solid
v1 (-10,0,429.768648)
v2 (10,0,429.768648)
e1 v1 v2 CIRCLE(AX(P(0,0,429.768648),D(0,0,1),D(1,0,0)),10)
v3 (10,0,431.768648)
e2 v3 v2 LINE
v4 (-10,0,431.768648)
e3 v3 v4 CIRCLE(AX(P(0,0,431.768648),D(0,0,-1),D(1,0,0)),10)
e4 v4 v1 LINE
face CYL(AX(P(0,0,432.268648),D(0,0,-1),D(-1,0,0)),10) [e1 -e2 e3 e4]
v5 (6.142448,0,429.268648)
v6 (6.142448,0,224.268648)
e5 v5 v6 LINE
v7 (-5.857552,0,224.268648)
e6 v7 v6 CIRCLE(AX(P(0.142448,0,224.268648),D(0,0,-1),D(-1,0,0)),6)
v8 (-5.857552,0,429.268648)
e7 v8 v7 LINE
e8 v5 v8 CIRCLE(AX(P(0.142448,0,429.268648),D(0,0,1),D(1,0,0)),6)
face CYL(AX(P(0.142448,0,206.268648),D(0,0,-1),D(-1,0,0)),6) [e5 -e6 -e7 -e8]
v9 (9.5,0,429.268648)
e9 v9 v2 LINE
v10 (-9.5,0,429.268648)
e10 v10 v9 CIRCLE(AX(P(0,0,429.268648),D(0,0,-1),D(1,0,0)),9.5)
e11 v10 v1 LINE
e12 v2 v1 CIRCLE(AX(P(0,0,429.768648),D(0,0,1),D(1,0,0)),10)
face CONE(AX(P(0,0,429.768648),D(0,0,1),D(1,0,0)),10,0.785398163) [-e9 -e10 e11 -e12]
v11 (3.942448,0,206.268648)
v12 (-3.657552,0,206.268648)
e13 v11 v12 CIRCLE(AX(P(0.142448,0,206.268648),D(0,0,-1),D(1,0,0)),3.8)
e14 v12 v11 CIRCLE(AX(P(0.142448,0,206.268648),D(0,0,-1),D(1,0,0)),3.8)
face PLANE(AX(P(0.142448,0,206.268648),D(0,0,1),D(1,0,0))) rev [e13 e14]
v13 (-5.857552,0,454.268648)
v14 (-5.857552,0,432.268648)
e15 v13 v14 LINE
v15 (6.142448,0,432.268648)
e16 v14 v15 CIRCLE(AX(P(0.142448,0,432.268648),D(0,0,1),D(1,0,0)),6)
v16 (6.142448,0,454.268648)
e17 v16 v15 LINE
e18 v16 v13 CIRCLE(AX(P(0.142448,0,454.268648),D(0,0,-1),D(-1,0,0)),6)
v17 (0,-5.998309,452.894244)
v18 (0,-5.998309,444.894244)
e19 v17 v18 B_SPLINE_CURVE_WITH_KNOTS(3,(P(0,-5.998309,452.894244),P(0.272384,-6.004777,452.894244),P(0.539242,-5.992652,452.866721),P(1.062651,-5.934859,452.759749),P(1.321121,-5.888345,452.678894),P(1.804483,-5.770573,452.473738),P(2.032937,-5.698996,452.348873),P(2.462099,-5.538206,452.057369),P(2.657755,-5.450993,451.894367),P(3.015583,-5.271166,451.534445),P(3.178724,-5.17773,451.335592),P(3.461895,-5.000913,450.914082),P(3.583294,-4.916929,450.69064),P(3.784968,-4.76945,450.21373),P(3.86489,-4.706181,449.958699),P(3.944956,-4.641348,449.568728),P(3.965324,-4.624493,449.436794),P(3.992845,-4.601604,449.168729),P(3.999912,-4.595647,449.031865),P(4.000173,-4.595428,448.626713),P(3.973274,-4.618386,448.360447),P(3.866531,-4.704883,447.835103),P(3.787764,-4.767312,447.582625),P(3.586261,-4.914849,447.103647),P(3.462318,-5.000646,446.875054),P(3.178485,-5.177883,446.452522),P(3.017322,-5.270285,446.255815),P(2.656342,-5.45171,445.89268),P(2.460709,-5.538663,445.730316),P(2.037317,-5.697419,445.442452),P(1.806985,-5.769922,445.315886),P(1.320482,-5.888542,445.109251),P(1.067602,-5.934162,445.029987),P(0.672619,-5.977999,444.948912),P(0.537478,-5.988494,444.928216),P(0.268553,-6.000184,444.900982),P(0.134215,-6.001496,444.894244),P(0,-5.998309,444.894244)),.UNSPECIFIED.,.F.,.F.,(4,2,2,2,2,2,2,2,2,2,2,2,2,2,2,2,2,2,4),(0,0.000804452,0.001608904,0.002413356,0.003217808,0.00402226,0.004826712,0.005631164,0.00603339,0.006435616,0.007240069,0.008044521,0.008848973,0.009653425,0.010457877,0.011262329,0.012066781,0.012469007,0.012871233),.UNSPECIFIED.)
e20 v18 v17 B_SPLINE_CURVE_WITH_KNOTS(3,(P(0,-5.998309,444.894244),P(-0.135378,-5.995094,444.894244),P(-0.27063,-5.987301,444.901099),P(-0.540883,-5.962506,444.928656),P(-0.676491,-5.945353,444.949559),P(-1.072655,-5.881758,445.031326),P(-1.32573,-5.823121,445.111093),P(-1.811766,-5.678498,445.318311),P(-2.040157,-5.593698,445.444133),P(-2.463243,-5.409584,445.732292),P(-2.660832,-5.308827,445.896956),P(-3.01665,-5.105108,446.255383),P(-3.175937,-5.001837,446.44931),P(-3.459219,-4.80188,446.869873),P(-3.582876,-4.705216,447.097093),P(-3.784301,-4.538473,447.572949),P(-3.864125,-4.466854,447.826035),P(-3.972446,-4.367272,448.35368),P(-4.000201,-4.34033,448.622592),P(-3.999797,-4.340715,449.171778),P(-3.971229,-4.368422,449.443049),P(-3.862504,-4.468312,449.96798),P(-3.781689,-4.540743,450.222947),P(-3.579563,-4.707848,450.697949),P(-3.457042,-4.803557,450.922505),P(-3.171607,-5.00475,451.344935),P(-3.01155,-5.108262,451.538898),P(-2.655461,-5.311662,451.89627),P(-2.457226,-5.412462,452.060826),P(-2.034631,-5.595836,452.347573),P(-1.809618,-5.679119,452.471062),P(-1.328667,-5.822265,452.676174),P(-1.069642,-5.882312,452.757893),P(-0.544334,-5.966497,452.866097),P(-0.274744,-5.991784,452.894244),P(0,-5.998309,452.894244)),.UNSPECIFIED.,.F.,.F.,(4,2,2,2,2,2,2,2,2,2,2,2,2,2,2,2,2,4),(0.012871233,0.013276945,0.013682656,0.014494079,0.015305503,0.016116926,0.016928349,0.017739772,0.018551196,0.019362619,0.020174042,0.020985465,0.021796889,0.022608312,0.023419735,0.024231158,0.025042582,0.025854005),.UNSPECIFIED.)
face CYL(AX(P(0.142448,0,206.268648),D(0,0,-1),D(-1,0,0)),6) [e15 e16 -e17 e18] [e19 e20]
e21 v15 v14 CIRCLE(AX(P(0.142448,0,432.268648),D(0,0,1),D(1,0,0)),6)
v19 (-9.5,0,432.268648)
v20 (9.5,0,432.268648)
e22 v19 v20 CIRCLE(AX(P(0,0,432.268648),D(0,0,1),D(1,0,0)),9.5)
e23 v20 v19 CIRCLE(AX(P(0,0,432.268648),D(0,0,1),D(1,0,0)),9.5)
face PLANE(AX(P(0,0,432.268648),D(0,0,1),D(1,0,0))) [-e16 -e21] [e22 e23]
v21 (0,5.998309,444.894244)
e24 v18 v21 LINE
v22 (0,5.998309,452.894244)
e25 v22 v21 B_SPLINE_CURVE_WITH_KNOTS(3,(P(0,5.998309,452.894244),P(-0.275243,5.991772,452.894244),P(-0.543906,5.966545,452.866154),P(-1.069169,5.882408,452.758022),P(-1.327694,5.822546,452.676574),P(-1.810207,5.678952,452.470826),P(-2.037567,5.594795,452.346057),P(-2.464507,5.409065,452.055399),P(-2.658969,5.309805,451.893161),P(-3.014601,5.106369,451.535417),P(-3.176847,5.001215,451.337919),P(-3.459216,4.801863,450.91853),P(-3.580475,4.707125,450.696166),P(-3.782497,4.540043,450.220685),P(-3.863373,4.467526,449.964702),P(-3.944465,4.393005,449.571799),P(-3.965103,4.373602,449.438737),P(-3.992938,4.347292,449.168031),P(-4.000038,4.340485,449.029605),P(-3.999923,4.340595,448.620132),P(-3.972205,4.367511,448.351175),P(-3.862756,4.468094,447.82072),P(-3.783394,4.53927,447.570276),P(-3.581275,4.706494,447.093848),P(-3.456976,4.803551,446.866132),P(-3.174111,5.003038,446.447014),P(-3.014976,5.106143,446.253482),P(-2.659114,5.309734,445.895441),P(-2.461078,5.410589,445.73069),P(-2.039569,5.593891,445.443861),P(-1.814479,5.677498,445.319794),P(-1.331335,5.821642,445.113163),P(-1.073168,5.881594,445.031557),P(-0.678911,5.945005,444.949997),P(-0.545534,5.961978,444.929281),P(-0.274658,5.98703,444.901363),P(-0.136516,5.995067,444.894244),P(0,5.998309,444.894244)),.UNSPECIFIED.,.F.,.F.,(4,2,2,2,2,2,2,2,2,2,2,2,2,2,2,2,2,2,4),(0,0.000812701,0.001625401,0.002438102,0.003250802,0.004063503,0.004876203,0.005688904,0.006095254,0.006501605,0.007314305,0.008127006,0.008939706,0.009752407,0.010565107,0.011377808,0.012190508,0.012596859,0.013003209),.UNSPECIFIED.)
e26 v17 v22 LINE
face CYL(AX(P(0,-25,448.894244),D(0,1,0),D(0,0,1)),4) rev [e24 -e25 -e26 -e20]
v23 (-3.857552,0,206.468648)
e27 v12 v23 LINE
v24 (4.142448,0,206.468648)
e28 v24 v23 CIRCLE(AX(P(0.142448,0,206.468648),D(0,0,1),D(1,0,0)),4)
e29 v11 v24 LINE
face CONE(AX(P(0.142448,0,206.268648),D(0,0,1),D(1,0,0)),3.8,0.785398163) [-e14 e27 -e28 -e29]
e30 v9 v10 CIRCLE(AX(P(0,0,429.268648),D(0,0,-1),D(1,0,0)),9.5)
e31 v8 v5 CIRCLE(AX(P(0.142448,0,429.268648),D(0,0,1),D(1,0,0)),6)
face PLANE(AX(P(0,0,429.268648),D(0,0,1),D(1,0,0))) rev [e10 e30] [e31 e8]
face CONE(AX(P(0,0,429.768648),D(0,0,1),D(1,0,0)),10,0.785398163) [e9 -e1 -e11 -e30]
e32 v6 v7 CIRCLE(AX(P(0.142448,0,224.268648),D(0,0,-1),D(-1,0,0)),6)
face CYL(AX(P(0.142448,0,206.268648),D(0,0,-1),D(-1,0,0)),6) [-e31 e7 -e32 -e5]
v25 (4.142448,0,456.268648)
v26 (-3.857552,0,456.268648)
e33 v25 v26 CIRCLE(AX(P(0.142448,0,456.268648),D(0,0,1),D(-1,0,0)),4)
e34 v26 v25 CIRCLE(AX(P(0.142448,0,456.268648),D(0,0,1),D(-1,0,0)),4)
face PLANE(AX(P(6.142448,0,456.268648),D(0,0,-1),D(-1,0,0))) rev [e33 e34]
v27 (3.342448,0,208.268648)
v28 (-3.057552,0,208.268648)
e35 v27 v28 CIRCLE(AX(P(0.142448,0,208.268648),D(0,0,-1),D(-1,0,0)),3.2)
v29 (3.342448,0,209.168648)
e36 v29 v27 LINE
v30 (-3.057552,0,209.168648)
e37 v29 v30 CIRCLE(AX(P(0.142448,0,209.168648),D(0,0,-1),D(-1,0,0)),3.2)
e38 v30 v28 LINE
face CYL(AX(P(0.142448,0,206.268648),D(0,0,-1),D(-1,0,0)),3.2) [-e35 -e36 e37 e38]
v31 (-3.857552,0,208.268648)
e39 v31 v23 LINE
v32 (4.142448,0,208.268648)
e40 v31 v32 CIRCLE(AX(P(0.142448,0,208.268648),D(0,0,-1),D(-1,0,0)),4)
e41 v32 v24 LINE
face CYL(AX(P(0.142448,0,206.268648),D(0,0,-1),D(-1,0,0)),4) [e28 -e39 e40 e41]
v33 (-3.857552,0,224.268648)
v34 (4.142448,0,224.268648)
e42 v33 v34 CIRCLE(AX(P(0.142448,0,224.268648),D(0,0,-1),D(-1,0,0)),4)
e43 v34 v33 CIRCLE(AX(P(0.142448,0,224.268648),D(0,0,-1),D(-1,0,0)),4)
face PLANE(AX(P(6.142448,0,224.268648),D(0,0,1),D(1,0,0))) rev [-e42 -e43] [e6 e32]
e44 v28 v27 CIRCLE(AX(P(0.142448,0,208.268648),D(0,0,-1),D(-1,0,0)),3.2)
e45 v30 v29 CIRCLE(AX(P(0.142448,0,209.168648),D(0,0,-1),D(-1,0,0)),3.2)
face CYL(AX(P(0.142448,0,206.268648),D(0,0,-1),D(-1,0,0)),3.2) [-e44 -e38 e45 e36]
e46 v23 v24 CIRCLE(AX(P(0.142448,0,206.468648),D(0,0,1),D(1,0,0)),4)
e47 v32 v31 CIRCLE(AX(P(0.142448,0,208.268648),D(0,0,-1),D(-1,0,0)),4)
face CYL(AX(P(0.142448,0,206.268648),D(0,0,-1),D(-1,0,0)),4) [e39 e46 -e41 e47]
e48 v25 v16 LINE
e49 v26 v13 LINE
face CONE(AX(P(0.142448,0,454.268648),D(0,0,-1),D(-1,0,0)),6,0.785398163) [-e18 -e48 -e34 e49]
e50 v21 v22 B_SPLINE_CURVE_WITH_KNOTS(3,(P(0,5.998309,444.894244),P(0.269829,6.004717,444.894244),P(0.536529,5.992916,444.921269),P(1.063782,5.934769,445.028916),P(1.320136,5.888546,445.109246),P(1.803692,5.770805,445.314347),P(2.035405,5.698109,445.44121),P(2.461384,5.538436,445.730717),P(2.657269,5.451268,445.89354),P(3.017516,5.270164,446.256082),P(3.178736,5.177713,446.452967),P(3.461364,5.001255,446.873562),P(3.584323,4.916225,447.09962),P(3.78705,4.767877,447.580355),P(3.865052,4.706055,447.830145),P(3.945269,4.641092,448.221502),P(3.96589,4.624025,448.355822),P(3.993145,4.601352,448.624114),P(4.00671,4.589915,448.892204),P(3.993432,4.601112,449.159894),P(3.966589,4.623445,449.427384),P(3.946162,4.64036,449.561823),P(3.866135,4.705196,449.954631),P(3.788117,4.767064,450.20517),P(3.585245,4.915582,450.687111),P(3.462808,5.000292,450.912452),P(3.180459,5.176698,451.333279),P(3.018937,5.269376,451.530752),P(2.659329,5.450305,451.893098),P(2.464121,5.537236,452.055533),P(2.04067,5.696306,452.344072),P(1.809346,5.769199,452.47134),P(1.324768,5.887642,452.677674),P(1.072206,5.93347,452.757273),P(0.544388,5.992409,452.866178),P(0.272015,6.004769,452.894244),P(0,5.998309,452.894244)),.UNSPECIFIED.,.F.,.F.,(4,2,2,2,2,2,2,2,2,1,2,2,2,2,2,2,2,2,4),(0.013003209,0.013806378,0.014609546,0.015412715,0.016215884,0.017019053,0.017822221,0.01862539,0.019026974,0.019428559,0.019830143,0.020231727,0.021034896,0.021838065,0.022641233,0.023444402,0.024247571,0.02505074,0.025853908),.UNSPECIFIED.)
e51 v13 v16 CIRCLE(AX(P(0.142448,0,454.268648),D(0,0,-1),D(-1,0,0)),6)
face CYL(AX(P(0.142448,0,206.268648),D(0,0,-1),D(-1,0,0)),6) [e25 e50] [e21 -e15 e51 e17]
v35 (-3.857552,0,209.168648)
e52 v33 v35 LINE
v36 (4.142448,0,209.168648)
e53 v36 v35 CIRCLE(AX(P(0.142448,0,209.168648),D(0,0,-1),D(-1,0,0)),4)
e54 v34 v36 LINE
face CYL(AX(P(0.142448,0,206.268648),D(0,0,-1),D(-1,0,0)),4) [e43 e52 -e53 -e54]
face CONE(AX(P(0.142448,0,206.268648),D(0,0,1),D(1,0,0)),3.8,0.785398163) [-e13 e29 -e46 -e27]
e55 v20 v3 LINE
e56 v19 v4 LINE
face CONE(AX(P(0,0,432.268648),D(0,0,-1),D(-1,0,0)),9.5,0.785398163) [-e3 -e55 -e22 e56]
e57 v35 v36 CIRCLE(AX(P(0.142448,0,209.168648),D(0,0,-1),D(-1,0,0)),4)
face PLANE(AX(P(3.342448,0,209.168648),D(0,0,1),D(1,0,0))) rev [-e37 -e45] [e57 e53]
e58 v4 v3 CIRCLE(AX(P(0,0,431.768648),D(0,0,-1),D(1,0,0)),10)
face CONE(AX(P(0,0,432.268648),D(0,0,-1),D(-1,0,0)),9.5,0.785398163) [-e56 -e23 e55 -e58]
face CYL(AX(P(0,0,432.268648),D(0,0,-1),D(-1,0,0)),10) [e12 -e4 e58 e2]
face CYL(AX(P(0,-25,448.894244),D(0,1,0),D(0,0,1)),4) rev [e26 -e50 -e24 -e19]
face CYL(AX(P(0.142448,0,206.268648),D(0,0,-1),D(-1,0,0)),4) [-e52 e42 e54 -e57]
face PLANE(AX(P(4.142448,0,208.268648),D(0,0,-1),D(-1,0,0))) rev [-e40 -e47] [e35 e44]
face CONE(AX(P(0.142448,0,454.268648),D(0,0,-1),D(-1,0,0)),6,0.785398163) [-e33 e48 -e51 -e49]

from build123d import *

# Parameters (mm, degrees)
SKETCH4_R          = 4
CUT_EXTRUDE2_DEPTH = 25
CHAMFER2_SIZE      = 2
CHAMFER3_SIZE      = 0.2
SKETCH5_R          = 10
BOSS_EXTRU_1_DEPTH = 3
CHAMFER4_SIZE      = 0.5


with BuildPart() as part:
    # Sketch1 → Revolve1 (revolve)
    with BuildSketch(Plane(origin=(0, 0, 0), x_dir=(1, 0, 0), z_dir=(0, 1, 0)), mode=Mode.PRIVATE) as revolve1_sk:
        Polygon((4.142447891, -208.268648203), (3.342447891, -208.268648203), (3.342447891, -209.168648203), (4.142447891, -209.168648203), (4.142447891, -224.268648203), (6.142447891, -224.268648203), (6.142447891, -456.268648203), (0.142447891, -456.268648203), (0.142447891, -206.268648203), (4.142447891, -206.268648203), align=None)
    revolve(revolve1_sk.sketch.rotate(Axis((0.142447891, 0, 206.268648203), (0, 0, 1)), 180), axis=Axis((0.142447891, 0, 206.268648203), (0, 0, 1)))

    # Sketch4 → Cut-Extrude2 (cut, symmetric)
    with BuildSketch(Plane(origin=(0, 0, 0), x_dir=(1, 0, 0), z_dir=(0, 1, 0))):
        with Locations(Location((0, -448.894244445, 0), (0, 0, 270))):
            Circle(SKETCH4_R)
    extrude(amount=CUT_EXTRUDE2_DEPTH, both=True, mode=Mode.SUBTRACT)

    # Chamfer2
    chamfer2_edges = [part.edges().sort_by_distance(p)[0] for p in [
        (6.142447891, 0, 456.268648203),
    ]]
    chamfer(chamfer2_edges, length=CHAMFER2_SIZE)

    # Chamfer3
    chamfer3_edges = [part.edges().sort_by_distance(p)[0] for p in [
        (4.142447891, 0, 206.268648203),
    ]]
    chamfer(chamfer3_edges, length=CHAMFER3_SIZE)

    # Sketch5 → Boss.-Extru.1 (add)
    with BuildSketch(Plane.XY.offset(429.268648203)):
        Circle(SKETCH5_R)
    extrude(amount=BOSS_EXTRU_1_DEPTH)

    # Chamfer4
    chamfer4_edges = [part.edges().sort_by_distance(p)[0] for p in [
        (-10, 0, 429.268648203),
        (-10, 0, 432.268648203),
    ]]
    chamfer(chamfer4_edges, length=CHAMFER4_SIZE)


solid = part.part
